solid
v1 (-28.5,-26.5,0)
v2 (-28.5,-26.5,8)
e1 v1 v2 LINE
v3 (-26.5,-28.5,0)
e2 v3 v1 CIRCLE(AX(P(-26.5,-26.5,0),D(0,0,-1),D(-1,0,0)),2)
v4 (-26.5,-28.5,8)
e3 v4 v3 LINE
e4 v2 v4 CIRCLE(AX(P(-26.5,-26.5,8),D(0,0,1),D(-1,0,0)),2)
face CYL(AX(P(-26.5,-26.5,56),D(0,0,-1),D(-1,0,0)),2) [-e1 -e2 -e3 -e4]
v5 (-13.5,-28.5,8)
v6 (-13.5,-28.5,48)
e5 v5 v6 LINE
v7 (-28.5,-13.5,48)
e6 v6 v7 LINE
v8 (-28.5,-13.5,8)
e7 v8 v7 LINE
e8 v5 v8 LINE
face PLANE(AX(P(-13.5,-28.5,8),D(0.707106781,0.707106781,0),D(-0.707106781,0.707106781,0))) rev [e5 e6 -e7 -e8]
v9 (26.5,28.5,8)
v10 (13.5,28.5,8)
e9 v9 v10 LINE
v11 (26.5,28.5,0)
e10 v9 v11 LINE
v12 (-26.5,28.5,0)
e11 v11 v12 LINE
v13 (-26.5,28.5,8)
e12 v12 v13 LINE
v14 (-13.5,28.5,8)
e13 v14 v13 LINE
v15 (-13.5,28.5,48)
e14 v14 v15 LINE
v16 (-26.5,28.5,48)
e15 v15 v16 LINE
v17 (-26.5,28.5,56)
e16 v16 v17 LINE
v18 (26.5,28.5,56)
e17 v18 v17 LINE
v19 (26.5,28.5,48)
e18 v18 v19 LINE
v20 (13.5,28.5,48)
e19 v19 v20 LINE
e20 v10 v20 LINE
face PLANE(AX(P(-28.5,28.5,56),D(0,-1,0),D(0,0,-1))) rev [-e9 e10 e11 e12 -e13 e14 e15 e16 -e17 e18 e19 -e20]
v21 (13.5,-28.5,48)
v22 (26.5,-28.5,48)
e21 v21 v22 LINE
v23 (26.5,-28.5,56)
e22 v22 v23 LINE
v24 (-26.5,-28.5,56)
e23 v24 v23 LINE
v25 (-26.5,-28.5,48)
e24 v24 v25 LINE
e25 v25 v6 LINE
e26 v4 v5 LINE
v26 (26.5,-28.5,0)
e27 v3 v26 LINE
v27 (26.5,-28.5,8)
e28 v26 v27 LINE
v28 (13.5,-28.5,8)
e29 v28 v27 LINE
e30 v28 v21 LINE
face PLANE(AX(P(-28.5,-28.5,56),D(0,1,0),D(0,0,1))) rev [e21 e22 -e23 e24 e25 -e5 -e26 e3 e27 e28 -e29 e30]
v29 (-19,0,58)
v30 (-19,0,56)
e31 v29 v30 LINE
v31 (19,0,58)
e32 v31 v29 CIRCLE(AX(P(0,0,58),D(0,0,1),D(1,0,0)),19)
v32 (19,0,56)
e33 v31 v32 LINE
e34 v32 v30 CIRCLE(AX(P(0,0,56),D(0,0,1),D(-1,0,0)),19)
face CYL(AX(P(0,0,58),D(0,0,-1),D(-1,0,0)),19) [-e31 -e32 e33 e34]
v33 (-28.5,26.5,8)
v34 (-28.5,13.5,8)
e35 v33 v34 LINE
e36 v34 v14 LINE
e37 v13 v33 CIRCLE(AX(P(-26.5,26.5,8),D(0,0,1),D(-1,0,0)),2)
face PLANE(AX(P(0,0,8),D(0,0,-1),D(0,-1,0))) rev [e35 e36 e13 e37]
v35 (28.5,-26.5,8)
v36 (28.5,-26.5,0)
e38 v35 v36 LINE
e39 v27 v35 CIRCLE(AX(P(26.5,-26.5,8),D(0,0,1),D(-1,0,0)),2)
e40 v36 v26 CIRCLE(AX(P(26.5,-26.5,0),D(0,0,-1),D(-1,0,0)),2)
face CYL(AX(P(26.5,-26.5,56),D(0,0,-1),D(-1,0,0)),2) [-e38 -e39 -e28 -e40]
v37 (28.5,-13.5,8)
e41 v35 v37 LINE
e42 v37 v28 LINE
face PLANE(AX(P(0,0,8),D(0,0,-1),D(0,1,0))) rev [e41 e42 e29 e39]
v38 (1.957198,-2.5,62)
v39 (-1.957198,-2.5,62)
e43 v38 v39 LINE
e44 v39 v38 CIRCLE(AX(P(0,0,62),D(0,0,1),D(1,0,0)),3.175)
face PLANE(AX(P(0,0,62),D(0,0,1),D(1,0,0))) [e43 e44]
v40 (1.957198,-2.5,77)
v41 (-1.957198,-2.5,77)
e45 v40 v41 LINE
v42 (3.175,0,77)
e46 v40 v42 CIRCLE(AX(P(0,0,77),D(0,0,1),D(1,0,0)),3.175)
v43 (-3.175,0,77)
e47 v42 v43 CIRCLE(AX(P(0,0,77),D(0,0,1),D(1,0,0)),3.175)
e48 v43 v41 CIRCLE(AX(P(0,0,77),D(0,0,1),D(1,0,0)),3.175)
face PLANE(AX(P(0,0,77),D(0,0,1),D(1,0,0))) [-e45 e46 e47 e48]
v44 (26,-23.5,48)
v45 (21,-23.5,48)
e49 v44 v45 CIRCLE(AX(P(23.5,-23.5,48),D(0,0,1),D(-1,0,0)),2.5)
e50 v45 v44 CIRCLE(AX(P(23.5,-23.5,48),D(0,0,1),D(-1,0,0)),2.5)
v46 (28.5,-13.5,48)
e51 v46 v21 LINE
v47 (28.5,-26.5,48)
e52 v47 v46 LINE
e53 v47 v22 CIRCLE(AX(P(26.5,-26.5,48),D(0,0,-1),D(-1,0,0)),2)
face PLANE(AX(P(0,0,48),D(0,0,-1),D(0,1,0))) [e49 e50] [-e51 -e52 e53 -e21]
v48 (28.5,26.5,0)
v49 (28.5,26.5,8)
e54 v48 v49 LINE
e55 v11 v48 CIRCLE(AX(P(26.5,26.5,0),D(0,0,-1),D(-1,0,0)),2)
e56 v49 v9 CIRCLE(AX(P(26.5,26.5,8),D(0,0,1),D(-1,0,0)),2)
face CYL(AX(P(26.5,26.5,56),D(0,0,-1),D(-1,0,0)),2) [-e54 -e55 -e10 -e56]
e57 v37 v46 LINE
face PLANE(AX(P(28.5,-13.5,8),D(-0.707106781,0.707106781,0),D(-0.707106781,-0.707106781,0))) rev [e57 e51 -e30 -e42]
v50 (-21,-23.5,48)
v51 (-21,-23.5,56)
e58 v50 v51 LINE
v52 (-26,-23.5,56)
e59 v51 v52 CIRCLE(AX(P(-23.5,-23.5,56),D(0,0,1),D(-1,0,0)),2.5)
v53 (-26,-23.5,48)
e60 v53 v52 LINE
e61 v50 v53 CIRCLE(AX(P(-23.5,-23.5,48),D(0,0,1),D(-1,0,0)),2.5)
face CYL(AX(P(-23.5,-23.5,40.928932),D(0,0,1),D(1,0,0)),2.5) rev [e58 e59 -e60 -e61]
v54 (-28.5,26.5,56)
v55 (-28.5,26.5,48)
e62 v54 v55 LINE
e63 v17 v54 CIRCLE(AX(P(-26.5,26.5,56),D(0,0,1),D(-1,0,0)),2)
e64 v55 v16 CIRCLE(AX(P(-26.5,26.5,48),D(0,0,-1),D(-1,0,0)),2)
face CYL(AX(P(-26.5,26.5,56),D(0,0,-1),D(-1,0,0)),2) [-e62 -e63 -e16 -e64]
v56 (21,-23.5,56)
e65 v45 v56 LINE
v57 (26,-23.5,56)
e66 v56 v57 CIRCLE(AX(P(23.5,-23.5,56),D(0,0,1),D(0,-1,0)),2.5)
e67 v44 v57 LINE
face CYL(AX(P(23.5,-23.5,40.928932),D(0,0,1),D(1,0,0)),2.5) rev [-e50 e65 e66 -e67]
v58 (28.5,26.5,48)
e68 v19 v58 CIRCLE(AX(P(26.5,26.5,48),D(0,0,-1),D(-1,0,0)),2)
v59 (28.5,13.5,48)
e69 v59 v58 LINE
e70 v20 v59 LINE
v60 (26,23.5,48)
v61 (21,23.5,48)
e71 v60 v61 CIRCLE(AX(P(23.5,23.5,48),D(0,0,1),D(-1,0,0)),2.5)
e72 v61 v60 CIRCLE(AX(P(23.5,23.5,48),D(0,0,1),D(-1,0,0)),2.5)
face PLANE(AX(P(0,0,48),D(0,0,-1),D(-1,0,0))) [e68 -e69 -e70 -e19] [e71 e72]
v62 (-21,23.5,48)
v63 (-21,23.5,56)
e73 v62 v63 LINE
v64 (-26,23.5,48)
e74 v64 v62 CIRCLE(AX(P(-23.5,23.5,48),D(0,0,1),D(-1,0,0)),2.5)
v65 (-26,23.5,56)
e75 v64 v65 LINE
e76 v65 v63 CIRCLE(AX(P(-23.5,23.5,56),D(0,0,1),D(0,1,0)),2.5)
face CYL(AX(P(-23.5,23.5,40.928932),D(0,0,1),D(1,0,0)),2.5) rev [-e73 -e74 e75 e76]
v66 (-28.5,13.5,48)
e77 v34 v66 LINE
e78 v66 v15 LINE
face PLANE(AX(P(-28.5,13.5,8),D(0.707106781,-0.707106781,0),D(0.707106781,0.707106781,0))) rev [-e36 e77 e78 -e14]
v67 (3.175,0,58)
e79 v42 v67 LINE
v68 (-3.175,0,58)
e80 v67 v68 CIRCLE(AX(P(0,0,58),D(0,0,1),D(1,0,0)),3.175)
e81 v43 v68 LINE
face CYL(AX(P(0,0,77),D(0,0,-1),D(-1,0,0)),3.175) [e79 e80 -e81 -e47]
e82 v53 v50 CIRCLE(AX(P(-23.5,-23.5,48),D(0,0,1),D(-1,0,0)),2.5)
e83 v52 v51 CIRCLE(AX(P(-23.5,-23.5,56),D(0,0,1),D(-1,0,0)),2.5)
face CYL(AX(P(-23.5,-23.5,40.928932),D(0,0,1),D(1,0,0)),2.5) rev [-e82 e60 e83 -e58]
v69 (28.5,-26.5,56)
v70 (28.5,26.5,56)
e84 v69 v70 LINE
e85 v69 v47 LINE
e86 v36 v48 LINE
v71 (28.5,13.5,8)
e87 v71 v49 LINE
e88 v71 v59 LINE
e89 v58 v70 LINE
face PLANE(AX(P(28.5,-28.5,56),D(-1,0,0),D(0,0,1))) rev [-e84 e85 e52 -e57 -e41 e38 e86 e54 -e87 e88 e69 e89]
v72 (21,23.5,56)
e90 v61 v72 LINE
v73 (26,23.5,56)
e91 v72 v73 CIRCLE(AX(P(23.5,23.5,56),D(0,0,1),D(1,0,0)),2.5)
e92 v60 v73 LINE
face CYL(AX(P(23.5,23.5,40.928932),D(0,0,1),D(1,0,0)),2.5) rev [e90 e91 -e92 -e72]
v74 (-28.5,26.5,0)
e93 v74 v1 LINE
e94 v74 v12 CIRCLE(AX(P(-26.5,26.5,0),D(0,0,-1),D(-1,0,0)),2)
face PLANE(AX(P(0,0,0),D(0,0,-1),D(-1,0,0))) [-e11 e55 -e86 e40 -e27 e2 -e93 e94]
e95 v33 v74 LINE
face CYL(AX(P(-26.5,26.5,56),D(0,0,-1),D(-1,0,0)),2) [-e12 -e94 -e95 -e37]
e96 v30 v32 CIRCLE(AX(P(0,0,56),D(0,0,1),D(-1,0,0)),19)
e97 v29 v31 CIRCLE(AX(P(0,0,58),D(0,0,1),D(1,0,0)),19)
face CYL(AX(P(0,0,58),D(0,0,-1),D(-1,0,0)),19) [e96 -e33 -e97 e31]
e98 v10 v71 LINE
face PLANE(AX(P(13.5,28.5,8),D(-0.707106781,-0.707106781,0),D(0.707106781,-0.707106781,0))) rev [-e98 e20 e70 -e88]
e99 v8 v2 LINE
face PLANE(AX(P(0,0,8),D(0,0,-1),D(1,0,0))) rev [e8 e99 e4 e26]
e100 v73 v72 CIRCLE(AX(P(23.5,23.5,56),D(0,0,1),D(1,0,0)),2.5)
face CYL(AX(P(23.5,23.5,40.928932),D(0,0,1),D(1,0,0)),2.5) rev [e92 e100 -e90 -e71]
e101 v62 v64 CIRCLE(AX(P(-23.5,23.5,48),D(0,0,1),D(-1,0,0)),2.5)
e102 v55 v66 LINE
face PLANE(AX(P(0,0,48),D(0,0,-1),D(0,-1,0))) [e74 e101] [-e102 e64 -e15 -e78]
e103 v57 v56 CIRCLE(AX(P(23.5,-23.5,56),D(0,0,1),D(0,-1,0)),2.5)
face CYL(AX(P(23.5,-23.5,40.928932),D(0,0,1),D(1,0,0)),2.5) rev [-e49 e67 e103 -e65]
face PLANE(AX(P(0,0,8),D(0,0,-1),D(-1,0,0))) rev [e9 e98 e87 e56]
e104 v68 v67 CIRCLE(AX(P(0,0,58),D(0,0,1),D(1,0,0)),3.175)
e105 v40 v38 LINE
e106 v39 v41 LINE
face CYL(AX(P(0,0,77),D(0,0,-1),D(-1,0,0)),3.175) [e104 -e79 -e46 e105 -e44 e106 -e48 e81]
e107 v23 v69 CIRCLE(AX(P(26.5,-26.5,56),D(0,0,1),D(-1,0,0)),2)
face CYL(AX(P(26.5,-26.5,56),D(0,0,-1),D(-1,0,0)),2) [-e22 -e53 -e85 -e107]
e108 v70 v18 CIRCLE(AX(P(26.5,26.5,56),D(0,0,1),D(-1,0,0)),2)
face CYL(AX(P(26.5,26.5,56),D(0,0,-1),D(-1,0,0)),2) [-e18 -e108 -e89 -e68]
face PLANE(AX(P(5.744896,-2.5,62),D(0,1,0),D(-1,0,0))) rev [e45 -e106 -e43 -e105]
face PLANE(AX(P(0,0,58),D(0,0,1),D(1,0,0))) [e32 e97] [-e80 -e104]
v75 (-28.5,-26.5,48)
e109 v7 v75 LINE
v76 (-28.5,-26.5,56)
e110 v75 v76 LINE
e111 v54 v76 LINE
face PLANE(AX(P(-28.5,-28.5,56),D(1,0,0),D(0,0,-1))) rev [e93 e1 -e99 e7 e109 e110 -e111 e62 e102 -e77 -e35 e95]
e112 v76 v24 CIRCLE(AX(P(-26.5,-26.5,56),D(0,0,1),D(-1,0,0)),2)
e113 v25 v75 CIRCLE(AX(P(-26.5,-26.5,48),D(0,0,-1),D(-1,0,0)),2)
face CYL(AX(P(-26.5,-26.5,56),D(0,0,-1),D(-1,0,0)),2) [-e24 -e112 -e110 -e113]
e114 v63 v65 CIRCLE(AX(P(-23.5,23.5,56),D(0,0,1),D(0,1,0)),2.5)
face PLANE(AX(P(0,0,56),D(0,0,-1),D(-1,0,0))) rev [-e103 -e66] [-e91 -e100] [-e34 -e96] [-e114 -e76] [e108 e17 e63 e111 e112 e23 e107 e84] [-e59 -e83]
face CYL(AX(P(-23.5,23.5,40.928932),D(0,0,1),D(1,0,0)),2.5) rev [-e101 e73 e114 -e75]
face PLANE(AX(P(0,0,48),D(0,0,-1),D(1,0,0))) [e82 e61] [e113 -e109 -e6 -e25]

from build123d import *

# Parameters (mm, degrees)
SKETCH_1_W               = 57
SKETCH_1_H               = 57
EXTRUDE_1_DEPTH          = 56
SKETCH_2_R               = 19
EXTRUDE_2_DEPTH          = 2
SKETCH_3_R               = 3.175
EXTRUDE_3_DEPTH          = 19
CUT_EXTRUDE_1_DEPTH      = 20
SKETCH_5_R               = 2.5
CUT_EXTRUDE_2_DEPTH      = 8
PATTERN_CIRCULAR_1_COUNT = 4
FILLET_1_R               = 2
SKETCH_6_W               = 11.376711671
SKETCH_6_H               = 3.467188319
CUT_EXTRUDE_3_DEPTH      = 15


with BuildPart() as part:
    # 草图1 → 凸台-拉伸1 (new body)
    with BuildSketch(Plane.XY):
        Rectangle(SKETCH_1_W, SKETCH_1_H)
    extrude(amount=EXTRUDE_1_DEPTH)

    # 草图2 → 凸台-拉伸2 (add)
    with BuildSketch(Plane.XY.offset(56)):
        with Locations(Location((0, 0, 0), (0, 0, 180))):
            Circle(SKETCH_2_R)
    extrude(amount=EXTRUDE_2_DEPTH)

    # 草图3 → 凸台-拉伸3 (add)
    with BuildSketch(Plane.XY.offset(58)):
        Circle(SKETCH_3_R)
    extrude(amount=EXTRUDE_3_DEPTH)

    # 草图4 → 切除-拉伸1 (cut, symmetric)
    with BuildSketch(Plane.XY.offset(28)):
        Polygon((13.5, 28.5), (28.5, 13.5), (28.5, 28.5), align=None)
    cut_extrude_1 = extrude(amount=CUT_EXTRUDE_1_DEPTH, both=True, mode=Mode.SUBTRACT)

    # 草图5 → 切除-拉伸2 (cut)
    with BuildSketch(Plane.XY.offset(56)):
        with Locations((23.5, 23.5)):
            Circle(SKETCH_5_R)
    cut_extrude_2 = extrude(amount=-CUT_EXTRUDE_2_DEPTH, mode=Mode.SUBTRACT)

    # 阵列(圆周)1: 切除-拉伸1, 切除-拉伸2 ×4 about axis
    pattern_circular_1_axis = Axis((0, 0, 0), (0, 0, 1))
    add([cut_extrude_1.rotate(pattern_circular_1_axis, i * 360 / PATTERN_CIRCULAR_1_COUNT) for i in range(1, PATTERN_CIRCULAR_1_COUNT)], mode=Mode.SUBTRACT)
    add([cut_extrude_2.rotate(pattern_circular_1_axis, i * 360 / PATTERN_CIRCULAR_1_COUNT) for i in range(1, PATTERN_CIRCULAR_1_COUNT)], mode=Mode.SUBTRACT)

    # 圆角1
    fillet_1_edges = [part.edges().sort_by_distance(p)[0] for p in [
        (28.5, 28.5, 4),
        (28.5, -28.5, 4),
        (-28.5, -28.5, 4),
        (-28.5, 28.5, 4),
        (28.5, -28.5, 52),
        (-28.5, -28.5, 52),
        (-28.5, 28.5, 52),
        (28.5, 28.5, 52),
    ]]
    fillet(fillet_1_edges, radius=FILLET_1_R)

    # 草图6 → 切除-拉伸3 (cut)
    with BuildSketch(Plane.XY.offset(77)):
        with Locations((0.056540367, -4.23359416)):
            Rectangle(SKETCH_6_W, SKETCH_6_H)
    extrude(amount=-CUT_EXTRUDE_3_DEPTH, mode=Mode.SUBTRACT)


solid = part.part
